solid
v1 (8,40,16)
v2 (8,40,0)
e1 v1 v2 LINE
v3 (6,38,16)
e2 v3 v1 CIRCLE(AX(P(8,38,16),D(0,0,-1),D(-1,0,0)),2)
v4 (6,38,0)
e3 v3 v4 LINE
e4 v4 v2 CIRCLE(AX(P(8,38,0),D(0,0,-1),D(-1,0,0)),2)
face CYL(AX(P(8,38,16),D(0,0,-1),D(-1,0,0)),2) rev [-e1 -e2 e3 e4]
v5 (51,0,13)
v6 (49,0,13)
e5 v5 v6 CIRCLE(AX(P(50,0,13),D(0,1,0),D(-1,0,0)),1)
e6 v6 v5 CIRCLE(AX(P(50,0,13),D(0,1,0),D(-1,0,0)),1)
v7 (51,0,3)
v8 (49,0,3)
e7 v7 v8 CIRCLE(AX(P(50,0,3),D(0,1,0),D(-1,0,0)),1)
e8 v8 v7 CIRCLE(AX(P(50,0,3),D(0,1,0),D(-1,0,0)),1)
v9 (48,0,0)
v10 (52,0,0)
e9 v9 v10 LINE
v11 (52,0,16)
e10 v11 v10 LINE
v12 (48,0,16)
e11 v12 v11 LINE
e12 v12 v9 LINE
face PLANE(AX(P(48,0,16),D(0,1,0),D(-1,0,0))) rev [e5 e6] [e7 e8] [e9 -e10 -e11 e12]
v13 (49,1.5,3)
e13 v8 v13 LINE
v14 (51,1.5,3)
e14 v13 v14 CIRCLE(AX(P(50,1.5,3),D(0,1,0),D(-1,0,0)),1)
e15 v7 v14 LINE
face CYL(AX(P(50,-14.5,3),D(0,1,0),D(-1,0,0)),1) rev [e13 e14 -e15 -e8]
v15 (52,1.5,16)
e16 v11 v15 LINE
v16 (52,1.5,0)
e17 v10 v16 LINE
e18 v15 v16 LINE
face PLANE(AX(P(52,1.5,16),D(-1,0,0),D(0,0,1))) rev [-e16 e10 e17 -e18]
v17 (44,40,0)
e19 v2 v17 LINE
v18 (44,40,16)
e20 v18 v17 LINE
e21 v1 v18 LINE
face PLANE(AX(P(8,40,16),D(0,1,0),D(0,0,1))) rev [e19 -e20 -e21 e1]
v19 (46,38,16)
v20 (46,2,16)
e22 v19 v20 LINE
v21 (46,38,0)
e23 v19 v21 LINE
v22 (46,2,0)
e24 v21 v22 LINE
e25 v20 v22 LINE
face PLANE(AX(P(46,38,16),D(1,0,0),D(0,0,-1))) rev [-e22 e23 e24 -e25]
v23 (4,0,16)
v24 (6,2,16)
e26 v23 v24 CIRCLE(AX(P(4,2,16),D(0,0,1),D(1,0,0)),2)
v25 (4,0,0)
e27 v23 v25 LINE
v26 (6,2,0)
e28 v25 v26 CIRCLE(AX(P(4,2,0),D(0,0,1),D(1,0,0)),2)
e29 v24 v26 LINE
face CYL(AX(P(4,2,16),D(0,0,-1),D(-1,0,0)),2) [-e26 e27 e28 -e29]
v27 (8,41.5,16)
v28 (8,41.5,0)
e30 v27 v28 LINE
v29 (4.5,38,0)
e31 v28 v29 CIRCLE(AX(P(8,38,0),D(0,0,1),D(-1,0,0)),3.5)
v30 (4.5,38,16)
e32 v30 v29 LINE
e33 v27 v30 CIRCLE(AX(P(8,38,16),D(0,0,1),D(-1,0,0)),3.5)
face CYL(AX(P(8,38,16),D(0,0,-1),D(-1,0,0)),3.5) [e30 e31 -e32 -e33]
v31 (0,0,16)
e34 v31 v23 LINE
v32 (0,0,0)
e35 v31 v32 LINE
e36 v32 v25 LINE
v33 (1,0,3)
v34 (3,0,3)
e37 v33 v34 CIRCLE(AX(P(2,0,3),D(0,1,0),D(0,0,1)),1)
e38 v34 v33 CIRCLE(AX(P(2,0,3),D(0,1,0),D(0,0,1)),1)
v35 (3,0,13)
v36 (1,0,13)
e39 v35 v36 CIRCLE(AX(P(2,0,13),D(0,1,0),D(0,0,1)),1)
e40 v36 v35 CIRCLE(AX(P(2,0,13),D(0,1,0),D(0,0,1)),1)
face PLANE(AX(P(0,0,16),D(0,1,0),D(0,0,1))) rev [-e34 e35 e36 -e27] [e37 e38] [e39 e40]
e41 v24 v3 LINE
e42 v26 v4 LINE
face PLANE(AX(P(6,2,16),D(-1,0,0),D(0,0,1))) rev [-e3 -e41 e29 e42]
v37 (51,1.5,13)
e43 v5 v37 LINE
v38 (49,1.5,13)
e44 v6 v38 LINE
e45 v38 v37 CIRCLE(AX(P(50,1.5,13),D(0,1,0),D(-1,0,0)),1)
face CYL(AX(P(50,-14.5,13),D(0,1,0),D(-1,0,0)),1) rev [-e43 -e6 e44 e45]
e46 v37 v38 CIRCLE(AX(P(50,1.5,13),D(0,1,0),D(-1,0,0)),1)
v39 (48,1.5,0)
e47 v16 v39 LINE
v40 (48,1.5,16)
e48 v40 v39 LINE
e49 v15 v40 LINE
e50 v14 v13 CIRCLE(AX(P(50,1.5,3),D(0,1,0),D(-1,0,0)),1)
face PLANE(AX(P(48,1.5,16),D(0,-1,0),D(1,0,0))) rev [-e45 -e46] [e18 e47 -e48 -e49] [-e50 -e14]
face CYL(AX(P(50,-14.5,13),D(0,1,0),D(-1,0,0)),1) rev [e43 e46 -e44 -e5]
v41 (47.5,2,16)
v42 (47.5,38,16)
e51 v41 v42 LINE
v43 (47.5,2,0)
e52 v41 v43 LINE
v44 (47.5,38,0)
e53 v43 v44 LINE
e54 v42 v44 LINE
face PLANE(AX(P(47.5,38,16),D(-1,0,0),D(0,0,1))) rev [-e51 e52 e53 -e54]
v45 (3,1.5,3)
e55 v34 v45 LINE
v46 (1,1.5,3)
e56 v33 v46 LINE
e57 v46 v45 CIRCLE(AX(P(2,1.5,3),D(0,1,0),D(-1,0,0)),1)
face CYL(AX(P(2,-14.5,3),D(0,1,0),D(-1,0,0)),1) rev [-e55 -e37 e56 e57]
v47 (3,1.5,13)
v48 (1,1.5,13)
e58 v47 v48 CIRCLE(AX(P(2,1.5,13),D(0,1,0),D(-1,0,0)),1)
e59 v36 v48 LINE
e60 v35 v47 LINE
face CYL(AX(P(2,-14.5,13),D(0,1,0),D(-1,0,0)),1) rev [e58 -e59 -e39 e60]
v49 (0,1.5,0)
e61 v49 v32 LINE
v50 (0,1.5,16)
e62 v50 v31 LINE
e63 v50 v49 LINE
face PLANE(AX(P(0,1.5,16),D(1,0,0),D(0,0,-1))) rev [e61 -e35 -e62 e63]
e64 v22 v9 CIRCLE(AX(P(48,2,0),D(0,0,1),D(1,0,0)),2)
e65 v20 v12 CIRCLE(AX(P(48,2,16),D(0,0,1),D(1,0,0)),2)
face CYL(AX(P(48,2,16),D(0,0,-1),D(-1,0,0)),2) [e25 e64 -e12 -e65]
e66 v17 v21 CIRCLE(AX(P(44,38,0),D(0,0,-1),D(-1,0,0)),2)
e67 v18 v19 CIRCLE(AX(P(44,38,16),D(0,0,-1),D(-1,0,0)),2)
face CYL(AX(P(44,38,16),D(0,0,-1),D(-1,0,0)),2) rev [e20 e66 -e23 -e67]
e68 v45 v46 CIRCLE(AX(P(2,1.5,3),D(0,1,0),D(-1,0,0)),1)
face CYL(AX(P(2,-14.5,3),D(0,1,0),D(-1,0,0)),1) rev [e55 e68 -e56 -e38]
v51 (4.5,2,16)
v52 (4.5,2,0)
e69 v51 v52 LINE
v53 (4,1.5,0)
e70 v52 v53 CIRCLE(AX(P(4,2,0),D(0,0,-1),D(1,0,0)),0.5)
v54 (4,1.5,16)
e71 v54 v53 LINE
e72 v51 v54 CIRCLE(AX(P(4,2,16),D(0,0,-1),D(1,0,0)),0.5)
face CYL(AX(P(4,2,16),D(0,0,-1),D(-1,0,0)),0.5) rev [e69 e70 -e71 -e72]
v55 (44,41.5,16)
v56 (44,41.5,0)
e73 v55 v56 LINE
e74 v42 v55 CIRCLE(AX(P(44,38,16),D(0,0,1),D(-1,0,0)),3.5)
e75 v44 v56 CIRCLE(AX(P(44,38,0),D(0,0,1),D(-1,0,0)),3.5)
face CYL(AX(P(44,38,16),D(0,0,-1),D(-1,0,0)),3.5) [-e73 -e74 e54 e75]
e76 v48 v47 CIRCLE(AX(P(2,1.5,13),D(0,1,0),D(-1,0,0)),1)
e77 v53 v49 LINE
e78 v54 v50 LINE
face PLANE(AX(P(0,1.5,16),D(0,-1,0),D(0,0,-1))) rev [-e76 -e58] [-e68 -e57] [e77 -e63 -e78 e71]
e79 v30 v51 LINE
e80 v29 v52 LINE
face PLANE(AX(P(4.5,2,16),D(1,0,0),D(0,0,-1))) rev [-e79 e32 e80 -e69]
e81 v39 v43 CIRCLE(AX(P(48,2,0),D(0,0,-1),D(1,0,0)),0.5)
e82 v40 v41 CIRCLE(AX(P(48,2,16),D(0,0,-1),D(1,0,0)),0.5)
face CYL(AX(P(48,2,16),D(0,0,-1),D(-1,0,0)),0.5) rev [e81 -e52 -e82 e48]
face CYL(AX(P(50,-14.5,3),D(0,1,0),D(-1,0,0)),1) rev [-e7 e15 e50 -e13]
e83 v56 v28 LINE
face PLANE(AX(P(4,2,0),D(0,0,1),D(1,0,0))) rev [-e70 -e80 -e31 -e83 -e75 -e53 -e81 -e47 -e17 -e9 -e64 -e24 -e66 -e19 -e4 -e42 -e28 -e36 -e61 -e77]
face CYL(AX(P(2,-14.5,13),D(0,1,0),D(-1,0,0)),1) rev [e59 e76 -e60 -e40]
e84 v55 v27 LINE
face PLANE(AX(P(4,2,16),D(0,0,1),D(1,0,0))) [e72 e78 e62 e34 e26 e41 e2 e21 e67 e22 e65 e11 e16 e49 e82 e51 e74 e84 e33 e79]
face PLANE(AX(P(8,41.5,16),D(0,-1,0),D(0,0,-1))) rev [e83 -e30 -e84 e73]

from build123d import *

# Parameters (mm, degrees)
BOSS_EXTRUDE1_DEPTH = 16
SKETCH2_R           = 1
CUT_EXTRUDE1_DEPTH  = 16


with BuildPart() as part:
    # Sketch1 → Boss-Extrude1 (new body)
    with BuildSketch(Plane.XY):
        with BuildLine():
            Line((0, 0), (4, 0))
            ThreePointArc((4, 0), (5.414213562, 0.585786438), (6, 2))
            Line((6, 2), (6, 38))
            ThreePointArc((6, 38), (6.585786438, 39.414213562), (8, 40))
            Line((8, 40), (44, 40))
            ThreePointArc((44, 40), (45.414213562, 39.414213562), (46, 38))
            Line((46, 38), (46, 2))
            ThreePointArc((46, 2), (46.585786438, 0.585786438), (48, 0))
            Line((48, 0), (52, 0))
            Line((52, 0), (52, 1.5))
            Line((52, 1.5), (48, 1.5))
            ThreePointArc((48, 1.5), (47.646446609, 1.646446609), (47.5, 2))
            Line((47.5, 2), (47.5, 38))
            ThreePointArc((47.5, 38), (46.474873734, 40.474873734), (44, 41.5))
            Line((44, 41.5), (8, 41.5))
            ThreePointArc((8, 41.5), (5.525126266, 40.474873734), (4.5, 38))
            Line((4.5, 38), (4.5, 2))
            ThreePointArc((4.5, 2), (4.353553391, 1.646446609), (4, 1.5))
            Line((4, 1.5), (0, 1.5))
            Line((0, 1.5), (0, 0))
        make_face()
    extrude(amount=BOSS_EXTRUDE1_DEPTH)

    # Sketch2 → Cut-Extrude1 (cut)
    with BuildSketch(Plane(origin=(0, 1.5, 0), x_dir=(1, 0, 0), z_dir=(0, 1, 0))):
        with Locations(Location((50, -3, 0), (0, 0, 180))):
            Circle(SKETCH2_R)
        with Locations(Location((50, -13, 0), (0, 0, 180))):
            Circle(SKETCH2_R)
        with Locations(Location((2, -3, 0), (0, 0, 180))):
            Circle(SKETCH2_R)
        with Locations(Location((2, -13, 0), (0, 0, 180))):
            Circle(SKETCH2_R)
    extrude(amount=-CUT_EXTRUDE1_DEPTH, mode=Mode.SUBTRACT)


solid = part.part
